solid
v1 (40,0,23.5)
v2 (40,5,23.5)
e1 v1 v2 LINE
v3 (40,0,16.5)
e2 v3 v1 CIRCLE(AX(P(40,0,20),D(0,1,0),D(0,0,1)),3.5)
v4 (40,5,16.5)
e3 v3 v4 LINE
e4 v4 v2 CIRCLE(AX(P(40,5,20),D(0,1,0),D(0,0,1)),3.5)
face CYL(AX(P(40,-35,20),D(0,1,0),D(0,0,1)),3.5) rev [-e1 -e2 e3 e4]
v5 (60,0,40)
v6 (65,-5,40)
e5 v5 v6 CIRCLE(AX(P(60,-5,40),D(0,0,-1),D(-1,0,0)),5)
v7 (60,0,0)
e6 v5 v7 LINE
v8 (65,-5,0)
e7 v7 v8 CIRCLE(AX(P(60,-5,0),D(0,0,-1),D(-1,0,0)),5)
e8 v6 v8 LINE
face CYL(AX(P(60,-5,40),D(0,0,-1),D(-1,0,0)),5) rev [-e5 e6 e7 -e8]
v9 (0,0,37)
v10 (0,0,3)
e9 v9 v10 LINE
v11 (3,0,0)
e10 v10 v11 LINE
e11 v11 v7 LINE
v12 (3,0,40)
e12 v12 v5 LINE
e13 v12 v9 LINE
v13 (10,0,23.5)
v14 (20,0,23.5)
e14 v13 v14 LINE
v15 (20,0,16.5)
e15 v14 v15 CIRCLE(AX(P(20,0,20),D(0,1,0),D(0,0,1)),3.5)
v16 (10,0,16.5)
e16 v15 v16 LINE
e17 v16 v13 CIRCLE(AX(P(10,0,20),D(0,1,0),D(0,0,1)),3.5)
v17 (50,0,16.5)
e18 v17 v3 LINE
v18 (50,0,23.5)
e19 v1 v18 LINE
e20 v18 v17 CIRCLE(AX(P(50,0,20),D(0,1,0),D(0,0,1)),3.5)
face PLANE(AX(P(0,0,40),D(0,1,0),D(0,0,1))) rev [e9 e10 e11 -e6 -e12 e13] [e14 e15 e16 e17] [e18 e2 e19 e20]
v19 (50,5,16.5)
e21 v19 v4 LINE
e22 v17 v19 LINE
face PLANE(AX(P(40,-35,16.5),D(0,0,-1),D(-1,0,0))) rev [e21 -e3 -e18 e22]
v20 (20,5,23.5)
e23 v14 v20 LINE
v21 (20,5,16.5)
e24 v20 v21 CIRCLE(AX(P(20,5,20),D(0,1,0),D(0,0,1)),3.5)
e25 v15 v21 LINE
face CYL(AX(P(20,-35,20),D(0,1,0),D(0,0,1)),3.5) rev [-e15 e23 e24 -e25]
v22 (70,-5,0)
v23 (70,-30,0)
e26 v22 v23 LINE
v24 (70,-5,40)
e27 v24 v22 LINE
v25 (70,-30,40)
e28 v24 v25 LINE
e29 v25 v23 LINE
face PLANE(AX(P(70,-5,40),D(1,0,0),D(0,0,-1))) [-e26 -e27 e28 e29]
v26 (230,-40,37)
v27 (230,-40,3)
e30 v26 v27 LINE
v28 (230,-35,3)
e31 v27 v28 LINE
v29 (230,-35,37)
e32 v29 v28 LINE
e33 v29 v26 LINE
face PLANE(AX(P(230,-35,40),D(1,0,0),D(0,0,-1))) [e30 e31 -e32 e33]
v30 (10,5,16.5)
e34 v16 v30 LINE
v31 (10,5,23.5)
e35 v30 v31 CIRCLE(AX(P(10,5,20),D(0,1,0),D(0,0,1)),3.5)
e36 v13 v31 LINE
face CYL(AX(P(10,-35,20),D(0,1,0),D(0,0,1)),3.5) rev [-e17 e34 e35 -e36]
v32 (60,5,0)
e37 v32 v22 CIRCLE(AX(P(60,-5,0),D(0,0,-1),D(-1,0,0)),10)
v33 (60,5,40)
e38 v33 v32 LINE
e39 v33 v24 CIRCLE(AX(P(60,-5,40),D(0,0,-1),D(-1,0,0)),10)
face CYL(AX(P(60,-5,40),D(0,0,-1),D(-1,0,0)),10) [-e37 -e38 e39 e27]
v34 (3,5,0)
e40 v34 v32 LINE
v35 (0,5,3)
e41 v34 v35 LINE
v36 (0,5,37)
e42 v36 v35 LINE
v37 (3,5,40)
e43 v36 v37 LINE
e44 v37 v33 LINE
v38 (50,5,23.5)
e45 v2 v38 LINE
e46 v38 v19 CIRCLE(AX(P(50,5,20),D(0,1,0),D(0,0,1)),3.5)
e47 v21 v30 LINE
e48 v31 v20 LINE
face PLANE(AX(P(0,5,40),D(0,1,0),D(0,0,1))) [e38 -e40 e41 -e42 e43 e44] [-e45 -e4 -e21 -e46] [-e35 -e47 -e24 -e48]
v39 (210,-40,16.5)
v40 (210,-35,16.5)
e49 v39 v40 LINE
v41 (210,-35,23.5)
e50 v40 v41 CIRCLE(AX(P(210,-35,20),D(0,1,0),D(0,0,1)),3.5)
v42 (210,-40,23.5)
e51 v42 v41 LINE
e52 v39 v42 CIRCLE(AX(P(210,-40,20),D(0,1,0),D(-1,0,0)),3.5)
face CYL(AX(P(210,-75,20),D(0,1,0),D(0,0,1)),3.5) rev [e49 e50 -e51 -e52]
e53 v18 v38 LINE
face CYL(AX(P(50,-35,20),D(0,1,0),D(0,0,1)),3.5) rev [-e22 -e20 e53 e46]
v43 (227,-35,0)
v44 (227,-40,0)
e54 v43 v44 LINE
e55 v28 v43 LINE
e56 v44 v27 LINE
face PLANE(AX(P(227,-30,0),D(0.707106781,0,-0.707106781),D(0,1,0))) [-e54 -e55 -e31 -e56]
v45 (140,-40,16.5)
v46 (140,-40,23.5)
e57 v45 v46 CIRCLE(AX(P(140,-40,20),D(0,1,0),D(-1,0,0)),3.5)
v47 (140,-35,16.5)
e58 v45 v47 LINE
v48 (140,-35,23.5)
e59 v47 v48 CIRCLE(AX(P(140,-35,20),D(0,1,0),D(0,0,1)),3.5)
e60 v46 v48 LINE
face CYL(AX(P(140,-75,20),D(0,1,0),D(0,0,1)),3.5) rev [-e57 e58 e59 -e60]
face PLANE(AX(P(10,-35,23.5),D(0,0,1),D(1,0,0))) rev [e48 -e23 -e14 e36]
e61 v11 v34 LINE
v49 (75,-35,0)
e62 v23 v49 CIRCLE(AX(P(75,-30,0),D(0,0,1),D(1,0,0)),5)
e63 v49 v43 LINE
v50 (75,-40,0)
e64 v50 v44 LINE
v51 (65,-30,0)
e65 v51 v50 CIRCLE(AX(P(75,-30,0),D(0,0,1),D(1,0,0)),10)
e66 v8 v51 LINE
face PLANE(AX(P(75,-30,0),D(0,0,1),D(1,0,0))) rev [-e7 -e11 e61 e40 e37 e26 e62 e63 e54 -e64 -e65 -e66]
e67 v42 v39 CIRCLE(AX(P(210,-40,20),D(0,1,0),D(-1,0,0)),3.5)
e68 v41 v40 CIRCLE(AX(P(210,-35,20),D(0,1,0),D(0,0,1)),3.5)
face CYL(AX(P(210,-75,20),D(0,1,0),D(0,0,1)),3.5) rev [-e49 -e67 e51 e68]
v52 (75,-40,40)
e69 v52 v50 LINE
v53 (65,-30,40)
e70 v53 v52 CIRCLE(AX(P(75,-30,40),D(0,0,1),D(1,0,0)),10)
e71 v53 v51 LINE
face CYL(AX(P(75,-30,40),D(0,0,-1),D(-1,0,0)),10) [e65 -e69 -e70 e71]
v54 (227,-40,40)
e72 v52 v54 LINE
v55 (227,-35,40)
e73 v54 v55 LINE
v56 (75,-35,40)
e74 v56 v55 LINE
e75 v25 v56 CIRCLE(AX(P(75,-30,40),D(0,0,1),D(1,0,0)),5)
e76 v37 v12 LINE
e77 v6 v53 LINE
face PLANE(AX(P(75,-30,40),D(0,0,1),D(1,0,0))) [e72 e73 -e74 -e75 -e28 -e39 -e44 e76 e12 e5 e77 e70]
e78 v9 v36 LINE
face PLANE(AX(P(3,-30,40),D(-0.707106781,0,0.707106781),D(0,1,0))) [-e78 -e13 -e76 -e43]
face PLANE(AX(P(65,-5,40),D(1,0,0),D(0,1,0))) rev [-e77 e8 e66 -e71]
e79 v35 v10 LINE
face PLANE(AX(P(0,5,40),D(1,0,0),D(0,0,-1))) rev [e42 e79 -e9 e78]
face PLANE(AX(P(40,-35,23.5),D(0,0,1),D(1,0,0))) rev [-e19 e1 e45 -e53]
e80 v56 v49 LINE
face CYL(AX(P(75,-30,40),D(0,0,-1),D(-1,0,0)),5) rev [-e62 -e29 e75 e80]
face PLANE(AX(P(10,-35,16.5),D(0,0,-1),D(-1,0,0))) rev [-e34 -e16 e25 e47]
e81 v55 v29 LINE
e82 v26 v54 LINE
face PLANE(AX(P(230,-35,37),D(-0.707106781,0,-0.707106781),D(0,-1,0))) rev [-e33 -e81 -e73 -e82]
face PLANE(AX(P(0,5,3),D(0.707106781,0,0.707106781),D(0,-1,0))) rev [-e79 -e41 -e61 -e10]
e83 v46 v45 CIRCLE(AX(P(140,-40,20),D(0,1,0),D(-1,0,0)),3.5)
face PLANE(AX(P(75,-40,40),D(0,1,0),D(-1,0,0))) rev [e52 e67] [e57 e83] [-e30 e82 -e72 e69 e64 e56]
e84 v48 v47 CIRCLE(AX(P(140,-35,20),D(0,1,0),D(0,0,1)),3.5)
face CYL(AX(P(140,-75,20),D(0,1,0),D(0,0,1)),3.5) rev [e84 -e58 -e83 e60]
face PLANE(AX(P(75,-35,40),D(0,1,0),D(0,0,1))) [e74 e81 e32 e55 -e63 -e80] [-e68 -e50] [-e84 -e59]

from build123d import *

# Parameters (mm, degrees)
BOSS_EXTRUDE1_DEPTH = 40
CUT_EXTRUDE1_DEPTH  = 40
SKETCH3_R           = 3.5
CUT_EXTRUDE2_DEPTH  = 40
CHAMFER1_SIZE       = 3


with BuildPart() as part:
    # Sketch1 → Boss-Extrude1 (new body)
    with BuildSketch(Plane.XY):
        with BuildLine():
            Line((0, 0), (60, 0))
            ThreePointArc((60, 0), (63.535533906, -1.464466094), (65, -5))
            Line((65, -5), (65, -30))
            ThreePointArc((65, -30), (67.928932188, -37.071067812), (75, -40))
            Line((75, -40), (230, -40))
            Line((230, -40), (230, -35))
            Line((230, -35), (75, -35))
            ThreePointArc((75, -35), (71.464466094, -33.535533906), (70, -30))
            Line((70, -30), (70, -5))
            ThreePointArc((70, -5), (67.071067812, 2.071067812), (60, 5))
            Line((60, 5), (0, 5))
            Line((0, 5), (0, 0))
        make_face()
    extrude(amount=BOSS_EXTRUDE1_DEPTH)

    # Sketch2 → Cut-Extrude1 (cut)
    with BuildSketch(Plane(origin=(0, 5, 0), x_dir=(1, 0, 0), z_dir=(0, 1, 0))):
        with BuildLine():
            Line((10, -16.5), (20, -16.5))
            ThreePointArc((20, -16.5), (23.5, -20), (20, -23.5))
            Line((20, -23.5), (10, -23.5))
            ThreePointArc((10, -23.5), (6.5, -20), (10, -16.5))
        make_face()
        with BuildLine():
            Line((40, -16.5), (50, -16.5))
            ThreePointArc((50, -16.5), (53.5, -20), (50, -23.5))
            Line((50, -23.5), (40, -23.5))
            ThreePointArc((40, -23.5), (36.5, -20), (40, -16.5))
        make_face()
    extrude(amount=-CUT_EXTRUDE1_DEPTH, mode=Mode.SUBTRACT)

    # Sketch3 → Cut-Extrude2 (cut)
    with BuildSketch(Plane(origin=(0, -35, 0), x_dir=(1, 0, 0), z_dir=(0, 1, 0))):
        with Locations(Location((140, -20, 0), (0, 0, 270))):
            Circle(SKETCH3_R)
        with Locations(Location((210, -20, 0), (0, 0, 270))):
            Circle(SKETCH3_R)
    extrude(amount=-CUT_EXTRUDE2_DEPTH, mode=Mode.SUBTRACT)

    # Chamfer1
    chamfer1_edges = [part.edges().sort_by_distance(p)[0] for p in [
        (0, 2.5, 0),
        (230, -37.5, 0),
        (0, 2.5, 40),
        (230, -37.5, 40),
    ]]
    chamfer(chamfer1_edges, length=CHAMFER1_SIZE)


solid = part.part
